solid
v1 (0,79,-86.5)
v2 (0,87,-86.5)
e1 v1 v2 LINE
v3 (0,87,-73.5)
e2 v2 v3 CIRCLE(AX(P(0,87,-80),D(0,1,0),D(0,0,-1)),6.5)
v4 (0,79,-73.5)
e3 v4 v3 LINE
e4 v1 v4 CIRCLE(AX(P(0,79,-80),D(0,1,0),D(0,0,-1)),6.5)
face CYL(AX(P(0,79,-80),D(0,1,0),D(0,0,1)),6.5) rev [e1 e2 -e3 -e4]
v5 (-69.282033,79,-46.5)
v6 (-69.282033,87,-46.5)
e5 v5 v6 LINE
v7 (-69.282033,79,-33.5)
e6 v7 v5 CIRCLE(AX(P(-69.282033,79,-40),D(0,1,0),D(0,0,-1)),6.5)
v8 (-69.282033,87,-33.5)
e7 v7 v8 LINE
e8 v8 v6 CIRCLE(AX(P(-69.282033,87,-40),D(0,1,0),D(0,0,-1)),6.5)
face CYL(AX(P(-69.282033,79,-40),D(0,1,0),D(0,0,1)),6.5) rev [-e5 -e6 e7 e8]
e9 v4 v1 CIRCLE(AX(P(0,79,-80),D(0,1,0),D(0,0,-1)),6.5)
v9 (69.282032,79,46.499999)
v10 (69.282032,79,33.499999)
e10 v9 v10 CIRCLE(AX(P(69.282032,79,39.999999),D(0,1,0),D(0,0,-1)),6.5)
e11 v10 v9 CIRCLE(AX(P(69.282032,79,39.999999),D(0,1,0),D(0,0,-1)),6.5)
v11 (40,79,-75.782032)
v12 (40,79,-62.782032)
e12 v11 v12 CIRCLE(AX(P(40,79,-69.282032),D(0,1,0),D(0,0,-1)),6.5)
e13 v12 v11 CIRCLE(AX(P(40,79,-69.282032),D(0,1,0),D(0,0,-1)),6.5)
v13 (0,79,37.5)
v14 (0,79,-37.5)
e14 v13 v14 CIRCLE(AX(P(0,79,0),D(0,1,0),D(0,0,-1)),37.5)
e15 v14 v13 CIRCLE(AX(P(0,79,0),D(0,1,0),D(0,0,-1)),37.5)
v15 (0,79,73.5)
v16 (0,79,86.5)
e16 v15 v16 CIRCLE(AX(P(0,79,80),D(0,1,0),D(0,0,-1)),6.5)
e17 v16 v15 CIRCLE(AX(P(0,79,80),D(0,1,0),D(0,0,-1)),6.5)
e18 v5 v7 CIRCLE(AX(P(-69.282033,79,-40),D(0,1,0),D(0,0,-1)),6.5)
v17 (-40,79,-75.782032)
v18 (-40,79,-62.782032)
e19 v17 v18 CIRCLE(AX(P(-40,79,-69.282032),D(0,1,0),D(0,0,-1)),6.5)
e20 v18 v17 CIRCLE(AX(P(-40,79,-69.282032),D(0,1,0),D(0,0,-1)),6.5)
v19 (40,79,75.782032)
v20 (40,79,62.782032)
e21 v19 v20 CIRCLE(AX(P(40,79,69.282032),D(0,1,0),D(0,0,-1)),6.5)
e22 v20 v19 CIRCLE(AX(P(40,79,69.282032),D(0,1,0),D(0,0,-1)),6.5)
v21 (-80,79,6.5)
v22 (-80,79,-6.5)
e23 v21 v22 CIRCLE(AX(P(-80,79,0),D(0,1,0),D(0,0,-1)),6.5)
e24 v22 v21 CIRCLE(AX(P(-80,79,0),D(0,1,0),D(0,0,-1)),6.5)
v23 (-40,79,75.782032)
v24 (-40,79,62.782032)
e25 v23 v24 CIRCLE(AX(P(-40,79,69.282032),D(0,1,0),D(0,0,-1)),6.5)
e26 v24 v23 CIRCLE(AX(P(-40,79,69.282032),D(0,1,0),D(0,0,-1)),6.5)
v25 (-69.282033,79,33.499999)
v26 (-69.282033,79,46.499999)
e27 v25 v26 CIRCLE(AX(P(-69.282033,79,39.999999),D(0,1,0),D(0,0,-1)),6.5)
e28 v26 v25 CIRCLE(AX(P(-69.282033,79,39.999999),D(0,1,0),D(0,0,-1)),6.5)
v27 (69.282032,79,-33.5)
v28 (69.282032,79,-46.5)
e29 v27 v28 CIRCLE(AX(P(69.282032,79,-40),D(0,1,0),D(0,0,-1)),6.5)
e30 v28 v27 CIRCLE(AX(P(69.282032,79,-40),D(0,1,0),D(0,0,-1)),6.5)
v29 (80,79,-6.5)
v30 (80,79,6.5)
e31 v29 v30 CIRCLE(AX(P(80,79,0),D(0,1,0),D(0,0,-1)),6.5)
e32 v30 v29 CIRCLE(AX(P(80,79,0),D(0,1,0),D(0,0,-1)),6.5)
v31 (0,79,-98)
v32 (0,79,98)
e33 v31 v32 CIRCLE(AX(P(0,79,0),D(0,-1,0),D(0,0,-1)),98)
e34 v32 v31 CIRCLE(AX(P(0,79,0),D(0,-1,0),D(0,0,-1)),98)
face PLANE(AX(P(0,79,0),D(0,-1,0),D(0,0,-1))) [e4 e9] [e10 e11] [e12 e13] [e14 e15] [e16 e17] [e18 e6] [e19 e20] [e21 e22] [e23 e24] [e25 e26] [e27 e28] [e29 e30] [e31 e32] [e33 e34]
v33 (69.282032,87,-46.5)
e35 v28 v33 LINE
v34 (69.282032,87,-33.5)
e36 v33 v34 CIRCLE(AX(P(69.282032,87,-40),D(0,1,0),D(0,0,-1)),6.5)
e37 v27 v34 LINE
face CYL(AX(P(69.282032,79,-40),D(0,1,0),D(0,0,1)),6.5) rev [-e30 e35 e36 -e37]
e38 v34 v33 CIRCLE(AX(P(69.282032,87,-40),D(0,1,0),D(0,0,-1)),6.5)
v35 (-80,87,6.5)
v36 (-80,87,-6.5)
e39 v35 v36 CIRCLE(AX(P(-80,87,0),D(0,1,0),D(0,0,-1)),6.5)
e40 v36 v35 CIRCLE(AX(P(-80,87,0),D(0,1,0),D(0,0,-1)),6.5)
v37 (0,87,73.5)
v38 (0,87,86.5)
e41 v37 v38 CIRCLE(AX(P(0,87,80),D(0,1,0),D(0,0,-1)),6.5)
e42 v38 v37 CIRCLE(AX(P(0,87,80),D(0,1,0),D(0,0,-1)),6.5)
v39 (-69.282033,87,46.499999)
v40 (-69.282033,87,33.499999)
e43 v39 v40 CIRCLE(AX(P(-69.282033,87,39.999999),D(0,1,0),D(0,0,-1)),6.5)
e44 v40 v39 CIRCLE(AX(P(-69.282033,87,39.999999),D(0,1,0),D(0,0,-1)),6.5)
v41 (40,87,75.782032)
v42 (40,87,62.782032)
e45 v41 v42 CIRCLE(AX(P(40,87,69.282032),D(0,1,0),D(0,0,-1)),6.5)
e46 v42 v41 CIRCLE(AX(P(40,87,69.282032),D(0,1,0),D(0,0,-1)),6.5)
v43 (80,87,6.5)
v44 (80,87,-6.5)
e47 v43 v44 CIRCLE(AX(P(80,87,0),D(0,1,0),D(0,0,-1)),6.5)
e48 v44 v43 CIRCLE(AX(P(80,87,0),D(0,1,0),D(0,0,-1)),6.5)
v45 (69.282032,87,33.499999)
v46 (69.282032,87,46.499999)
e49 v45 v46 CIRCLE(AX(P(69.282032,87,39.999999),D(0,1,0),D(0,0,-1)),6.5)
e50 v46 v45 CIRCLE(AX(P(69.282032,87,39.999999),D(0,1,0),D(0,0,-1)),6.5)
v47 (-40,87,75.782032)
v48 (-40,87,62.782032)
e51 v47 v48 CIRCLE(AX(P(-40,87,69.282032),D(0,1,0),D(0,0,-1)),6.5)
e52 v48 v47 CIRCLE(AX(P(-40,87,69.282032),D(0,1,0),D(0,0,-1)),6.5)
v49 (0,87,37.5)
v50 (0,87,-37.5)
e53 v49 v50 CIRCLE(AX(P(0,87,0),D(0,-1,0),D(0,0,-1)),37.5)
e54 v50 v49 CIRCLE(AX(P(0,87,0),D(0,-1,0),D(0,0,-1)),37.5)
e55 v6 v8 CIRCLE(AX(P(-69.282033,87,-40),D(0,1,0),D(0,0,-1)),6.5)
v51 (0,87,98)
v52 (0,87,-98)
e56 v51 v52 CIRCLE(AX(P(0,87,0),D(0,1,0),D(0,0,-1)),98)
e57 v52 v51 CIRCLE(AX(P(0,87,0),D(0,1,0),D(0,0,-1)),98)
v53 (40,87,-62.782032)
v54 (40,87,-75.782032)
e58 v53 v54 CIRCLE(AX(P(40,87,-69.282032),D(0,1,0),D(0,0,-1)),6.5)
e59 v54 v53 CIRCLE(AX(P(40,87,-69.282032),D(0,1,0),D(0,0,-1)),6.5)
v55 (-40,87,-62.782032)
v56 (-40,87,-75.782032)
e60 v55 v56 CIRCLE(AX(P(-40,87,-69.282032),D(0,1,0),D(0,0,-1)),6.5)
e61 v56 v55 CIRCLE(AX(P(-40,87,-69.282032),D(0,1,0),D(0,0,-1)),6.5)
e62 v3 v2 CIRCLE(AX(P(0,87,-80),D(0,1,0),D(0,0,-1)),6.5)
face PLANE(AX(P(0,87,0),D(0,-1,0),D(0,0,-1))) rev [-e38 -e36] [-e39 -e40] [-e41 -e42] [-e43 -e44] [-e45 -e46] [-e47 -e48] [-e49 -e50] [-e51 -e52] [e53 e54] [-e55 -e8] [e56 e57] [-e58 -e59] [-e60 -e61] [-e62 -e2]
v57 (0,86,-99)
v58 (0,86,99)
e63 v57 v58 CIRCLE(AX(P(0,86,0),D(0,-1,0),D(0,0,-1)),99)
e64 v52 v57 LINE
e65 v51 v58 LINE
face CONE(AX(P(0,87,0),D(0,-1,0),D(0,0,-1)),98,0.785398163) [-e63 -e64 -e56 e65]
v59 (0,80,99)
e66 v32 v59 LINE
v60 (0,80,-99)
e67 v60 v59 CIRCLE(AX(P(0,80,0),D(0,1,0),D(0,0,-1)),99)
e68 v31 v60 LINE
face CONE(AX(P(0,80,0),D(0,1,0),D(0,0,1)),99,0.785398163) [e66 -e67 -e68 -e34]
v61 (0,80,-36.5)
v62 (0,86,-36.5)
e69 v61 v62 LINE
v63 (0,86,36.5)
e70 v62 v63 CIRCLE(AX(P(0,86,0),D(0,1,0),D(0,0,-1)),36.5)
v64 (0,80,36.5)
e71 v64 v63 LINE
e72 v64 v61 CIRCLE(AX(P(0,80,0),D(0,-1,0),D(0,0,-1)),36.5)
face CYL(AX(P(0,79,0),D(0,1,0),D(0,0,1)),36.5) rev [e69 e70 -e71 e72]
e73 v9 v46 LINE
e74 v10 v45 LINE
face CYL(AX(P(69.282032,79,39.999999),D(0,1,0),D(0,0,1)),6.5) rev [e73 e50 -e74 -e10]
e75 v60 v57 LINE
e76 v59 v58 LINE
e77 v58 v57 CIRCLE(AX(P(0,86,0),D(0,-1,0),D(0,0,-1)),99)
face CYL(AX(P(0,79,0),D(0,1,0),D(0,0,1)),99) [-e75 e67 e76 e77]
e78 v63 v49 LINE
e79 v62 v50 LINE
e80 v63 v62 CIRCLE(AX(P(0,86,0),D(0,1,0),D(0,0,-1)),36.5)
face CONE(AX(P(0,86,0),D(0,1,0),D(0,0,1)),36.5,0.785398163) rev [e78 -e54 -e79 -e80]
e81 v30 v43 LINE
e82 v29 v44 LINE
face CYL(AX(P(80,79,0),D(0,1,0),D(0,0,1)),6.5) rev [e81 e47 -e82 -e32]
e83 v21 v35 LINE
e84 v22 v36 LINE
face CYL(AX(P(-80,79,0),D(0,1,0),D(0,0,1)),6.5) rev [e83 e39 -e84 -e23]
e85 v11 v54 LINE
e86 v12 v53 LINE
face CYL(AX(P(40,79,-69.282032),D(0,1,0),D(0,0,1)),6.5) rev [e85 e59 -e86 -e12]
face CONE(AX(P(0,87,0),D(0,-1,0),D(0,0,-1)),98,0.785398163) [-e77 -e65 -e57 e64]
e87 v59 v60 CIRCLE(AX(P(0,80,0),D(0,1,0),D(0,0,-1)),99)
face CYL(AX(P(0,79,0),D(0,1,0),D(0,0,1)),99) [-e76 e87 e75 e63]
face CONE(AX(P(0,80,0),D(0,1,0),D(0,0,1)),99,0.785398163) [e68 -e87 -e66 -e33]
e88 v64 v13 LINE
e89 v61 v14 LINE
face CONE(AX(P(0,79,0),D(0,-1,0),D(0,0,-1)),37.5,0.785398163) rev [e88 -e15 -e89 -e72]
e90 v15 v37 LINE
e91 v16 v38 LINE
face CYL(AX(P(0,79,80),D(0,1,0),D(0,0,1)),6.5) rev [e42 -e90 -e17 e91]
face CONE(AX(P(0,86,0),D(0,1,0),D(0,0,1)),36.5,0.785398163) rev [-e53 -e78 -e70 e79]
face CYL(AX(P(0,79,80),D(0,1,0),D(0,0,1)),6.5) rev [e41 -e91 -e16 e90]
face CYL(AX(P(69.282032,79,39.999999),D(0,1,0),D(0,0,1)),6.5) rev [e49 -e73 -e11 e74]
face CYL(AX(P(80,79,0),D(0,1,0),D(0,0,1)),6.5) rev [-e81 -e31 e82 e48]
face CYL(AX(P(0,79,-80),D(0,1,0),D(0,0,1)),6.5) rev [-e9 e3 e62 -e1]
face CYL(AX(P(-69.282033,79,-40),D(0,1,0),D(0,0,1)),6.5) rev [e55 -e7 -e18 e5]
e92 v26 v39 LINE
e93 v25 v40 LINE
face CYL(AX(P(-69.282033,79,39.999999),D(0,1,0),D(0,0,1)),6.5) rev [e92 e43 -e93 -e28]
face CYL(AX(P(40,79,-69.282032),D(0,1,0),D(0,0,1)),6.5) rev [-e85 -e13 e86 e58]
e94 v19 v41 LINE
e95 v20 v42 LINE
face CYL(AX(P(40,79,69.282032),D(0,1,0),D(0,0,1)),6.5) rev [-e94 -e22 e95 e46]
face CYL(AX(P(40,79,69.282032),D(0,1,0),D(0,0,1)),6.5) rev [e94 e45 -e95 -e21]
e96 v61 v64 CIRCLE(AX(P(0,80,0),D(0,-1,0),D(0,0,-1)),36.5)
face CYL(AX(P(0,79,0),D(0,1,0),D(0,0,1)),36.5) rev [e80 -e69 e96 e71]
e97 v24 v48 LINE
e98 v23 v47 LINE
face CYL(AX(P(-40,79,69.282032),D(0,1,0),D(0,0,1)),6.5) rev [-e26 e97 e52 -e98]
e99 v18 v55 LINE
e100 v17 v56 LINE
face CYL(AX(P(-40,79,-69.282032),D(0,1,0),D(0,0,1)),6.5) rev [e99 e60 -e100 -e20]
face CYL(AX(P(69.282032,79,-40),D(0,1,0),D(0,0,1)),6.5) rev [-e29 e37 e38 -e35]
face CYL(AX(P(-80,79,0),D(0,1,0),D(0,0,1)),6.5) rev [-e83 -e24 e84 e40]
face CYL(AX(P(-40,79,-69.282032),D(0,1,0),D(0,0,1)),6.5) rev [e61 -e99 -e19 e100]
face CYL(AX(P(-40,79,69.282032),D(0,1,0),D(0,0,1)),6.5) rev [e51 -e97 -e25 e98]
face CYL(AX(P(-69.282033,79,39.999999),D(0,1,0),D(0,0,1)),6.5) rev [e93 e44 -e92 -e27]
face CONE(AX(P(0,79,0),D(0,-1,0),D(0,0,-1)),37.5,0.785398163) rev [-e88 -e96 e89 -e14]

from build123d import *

# Parameters (mm, degrees)
SKETCH_1_R      = 99
SKETCH_1_R_2    = 6.5
SKETCH_1_R_3    = 36.5
EXTRUDE_1_DEPTH = 8
CHAMFER_1_SIZE  = 1


with BuildPart() as part:
    # 草图1 → 凸台-拉伸1 (new body)
    with BuildSketch(Plane(origin=(0, 87, 0), x_dir=(1, 0, 0), z_dir=(0, 1, 0))):
        with Locations(Location((0, 0, 0), (0, 0, 90))):
            Circle(SKETCH_1_R)
        with Locations(Location((-80, 0, 0), (0, 0, 90))):
            Circle(SKETCH_1_R_2, mode=Mode.SUBTRACT)
        with Locations(Location((40, 69.282032303, 0), (0, 0, 90))):
            Circle(SKETCH_1_R_2, mode=Mode.SUBTRACT)
        with Locations(Location((-69.282032733, 40, 0), (0, 0, 90))):
            Circle(SKETCH_1_R_2, mode=Mode.SUBTRACT)
        with Locations(Location((-69.282032733, -39.999999255, 0), (0, 0, 90))):
            Circle(SKETCH_1_R_2, mode=Mode.SUBTRACT)
        with Locations(Location((0, 80, 0), (0, 0, 90))):
            Circle(SKETCH_1_R_2, mode=Mode.SUBTRACT)
        with Locations(Location((69.282032302, -39.999999255, 0), (0, 0, 90))):
            Circle(SKETCH_1_R_2, mode=Mode.SUBTRACT)
        with Locations(Location((-40, 69.282032303, 0), (0, 0, 90))):
            Circle(SKETCH_1_R_2, mode=Mode.SUBTRACT)
        with Locations(Location((0, -80, 0), (0, 0, 90))):
            Circle(SKETCH_1_R_2, mode=Mode.SUBTRACT)
        with Locations(Location((40, -69.282032303, 0), (0, 0, 90))):
            Circle(SKETCH_1_R_2, mode=Mode.SUBTRACT)
        with Locations(Location((69.282032302, 40, 0), (0, 0, 90))):
            Circle(SKETCH_1_R_2, mode=Mode.SUBTRACT)
        with Locations(Location((-40, -69.282032303, 0), (0, 0, 90))):
            Circle(SKETCH_1_R_2, mode=Mode.SUBTRACT)
        with Locations(Location((80, 0, 0), (0, 0, 90))):
            Circle(SKETCH_1_R_2, mode=Mode.SUBTRACT)
        with Locations(Location((0, 0, 0), (0, 0, 90))):
            Circle(SKETCH_1_R_3, mode=Mode.SUBTRACT)
    extrude(amount=-EXTRUDE_1_DEPTH)

    # 倒角1
    chamfer_1_edges = [part.edges().sort_by_distance(p)[0] for p in [
        (0, 87, 99),
        (0, 79, 99),
        (0, 79, 36.5),
        (0, 87, 36.5),
    ]]
    chamfer(chamfer_1_edges, length=CHAMFER_1_SIZE)


solid = part.part
